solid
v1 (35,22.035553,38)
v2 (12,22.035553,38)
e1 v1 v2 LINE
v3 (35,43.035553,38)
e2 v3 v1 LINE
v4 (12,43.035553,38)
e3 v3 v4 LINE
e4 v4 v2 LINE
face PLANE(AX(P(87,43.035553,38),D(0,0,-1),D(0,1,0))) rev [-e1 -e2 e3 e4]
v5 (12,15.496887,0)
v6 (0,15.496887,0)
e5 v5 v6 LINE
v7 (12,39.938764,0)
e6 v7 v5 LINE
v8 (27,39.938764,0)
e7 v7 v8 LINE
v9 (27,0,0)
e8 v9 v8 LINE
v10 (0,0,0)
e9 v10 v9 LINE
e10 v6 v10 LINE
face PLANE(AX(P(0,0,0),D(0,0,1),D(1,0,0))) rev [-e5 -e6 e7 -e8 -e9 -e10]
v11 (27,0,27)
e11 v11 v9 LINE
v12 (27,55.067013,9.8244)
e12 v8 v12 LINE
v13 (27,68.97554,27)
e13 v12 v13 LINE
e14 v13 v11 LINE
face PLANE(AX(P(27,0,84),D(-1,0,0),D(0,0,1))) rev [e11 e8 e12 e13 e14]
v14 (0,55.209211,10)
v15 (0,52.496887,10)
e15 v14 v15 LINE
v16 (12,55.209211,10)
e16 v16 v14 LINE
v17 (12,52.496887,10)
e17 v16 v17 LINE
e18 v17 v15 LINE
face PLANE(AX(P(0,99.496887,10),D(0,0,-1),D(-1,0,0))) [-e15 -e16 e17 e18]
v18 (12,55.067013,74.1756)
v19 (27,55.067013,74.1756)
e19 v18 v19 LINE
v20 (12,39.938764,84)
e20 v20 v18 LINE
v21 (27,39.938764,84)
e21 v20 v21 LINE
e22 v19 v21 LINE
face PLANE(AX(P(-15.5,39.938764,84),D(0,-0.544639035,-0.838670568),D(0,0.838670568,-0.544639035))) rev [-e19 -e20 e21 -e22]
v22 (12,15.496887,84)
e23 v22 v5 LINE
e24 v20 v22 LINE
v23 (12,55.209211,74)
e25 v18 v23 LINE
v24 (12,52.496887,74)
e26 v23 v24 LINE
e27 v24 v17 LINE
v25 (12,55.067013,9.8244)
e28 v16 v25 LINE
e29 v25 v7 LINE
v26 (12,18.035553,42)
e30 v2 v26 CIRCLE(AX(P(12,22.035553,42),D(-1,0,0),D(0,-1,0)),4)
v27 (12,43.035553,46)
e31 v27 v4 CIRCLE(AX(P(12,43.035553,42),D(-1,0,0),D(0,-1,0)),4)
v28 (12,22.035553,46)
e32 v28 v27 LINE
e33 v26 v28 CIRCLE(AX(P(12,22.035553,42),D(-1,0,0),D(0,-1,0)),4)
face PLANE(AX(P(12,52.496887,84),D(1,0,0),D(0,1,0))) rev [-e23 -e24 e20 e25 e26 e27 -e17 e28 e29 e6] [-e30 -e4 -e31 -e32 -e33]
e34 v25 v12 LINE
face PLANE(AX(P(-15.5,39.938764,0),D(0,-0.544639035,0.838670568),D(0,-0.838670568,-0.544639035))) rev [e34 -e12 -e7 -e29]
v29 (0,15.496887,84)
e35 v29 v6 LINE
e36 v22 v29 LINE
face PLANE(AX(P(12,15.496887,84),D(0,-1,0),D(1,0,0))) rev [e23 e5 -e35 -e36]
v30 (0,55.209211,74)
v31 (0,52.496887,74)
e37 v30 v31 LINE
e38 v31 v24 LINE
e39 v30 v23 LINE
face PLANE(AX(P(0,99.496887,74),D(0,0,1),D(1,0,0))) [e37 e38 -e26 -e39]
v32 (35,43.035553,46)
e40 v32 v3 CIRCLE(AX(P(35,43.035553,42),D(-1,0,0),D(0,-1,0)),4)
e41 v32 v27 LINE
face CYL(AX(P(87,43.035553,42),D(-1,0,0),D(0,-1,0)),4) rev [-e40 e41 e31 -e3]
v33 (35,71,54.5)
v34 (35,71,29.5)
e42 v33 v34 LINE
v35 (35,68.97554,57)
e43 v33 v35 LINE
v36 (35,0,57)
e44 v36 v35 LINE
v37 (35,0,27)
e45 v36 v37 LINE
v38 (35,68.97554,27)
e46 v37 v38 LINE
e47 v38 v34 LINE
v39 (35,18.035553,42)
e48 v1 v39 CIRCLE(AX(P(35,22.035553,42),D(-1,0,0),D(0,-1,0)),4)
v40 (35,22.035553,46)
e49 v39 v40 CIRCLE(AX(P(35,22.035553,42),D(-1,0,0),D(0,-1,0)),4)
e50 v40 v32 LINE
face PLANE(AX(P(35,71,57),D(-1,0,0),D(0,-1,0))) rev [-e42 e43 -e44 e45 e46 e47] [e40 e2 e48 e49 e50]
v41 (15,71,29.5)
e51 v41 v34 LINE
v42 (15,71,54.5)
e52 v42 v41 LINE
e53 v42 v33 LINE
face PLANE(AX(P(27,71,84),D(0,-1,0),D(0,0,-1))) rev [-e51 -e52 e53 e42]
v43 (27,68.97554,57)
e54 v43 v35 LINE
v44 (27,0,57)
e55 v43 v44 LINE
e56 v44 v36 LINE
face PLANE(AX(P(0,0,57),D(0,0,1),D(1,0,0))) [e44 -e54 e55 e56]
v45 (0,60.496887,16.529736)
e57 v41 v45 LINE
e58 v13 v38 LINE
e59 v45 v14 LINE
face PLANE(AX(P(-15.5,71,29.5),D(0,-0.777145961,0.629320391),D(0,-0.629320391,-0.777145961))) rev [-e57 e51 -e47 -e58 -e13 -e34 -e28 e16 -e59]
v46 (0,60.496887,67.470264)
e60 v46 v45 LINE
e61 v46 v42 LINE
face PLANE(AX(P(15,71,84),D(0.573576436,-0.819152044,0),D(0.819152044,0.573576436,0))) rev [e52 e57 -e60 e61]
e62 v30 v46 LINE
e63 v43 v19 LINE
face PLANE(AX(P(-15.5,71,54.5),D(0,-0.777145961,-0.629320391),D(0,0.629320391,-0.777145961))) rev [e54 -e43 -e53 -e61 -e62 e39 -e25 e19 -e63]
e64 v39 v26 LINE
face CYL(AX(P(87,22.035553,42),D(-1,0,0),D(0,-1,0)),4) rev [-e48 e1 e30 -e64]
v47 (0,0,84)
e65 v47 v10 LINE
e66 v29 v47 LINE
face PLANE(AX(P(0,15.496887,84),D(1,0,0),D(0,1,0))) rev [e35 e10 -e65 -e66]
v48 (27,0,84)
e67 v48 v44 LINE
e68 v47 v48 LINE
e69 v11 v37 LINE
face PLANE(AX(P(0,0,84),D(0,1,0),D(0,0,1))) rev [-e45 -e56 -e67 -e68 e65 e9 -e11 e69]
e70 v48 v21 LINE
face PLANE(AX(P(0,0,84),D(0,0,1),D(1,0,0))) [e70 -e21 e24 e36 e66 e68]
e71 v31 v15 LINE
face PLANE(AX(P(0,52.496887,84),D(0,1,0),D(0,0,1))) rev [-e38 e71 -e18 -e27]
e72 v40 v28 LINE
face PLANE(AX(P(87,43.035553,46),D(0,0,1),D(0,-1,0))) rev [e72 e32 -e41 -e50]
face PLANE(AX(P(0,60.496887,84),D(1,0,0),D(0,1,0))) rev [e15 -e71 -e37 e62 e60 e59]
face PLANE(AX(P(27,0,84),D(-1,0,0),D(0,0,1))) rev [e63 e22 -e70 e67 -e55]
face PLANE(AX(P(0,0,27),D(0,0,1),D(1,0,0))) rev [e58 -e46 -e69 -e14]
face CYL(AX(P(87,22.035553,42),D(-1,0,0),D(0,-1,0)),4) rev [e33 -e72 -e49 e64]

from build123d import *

# Parameters (mm, degrees)
BASE_BLOCK_84MM_DEPTH  = 84
BACK_CHANNEL_SKETCH_W  = 12
BACK_CHANNEL_SKETCH_H  = 10
BACK_CHANNEL_CUT_DEPTH = 84
FRONT_PAD_SKETCH_W     = 8
FRONT_PAD_SKETCH_H     = 71
FRONT_PAD_8MM_DEPTH    = 15
TOP_CHAMFER_CUT_DEPTH  = 42.5
SLOT_CUT_DEPTH         = 75


with BuildPart() as part:
    # Block Profile Sketch → Base Block 84mm (new body)
    with BuildSketch(Plane.XY):
        Polygon((0, 0), (27, 0), (27, 71), (15, 71), (0, 60.496886927), (0, 52.496886927), (12, 52.496886927), (12, 15.496886927), (0, 15.496886927), align=None)
    extrude(amount=BASE_BLOCK_84MM_DEPTH)

    # Back Channel Sketch → Back Channel Cut (cut)
    with BuildSketch(Plane(origin=(0, 15.496886927, 0), x_dir=(1, 0, 0), z_dir=(0, 1, 0))):
        with Locations((6, -79)):
            Rectangle(BACK_CHANNEL_SKETCH_W, BACK_CHANNEL_SKETCH_H)
        with Locations((6, -5)):
            Rectangle(BACK_CHANNEL_SKETCH_W, BACK_CHANNEL_SKETCH_H)
    extrude(amount=BACK_CHANNEL_CUT_DEPTH, mode=Mode.SUBTRACT)

    # Front Pad Sketch → Front Pad 8mm (add, symmetric)
    with BuildSketch(Plane.XY.offset(42)):
        with Locations((31, 35.5)):
            Rectangle(FRONT_PAD_SKETCH_W, FRONT_PAD_SKETCH_H)
    extrude(amount=FRONT_PAD_8MM_DEPTH, both=True)

    # Top Chamfer Sketch → Top Chamfer Cut (cut, symmetric)
    with BuildSketch(Plane(origin=(27, 0, 0), x_dir=(0, 0, -1), z_dir=(1, 0, 0))):
        Polygon((-54.5, 71), (-74.175600087, 55.067013206), (-84, 39.938763989), (-84, 71), align=None)
        Polygon((-29.5, 71), (-9.824399913, 55.067013206), (0, 39.938763989), (0, 71), align=None)
    extrude(amount=TOP_CHAMFER_CUT_DEPTH, both=True, mode=Mode.SUBTRACT)

    # Slot Sketch → Slot Cut (cut)
    with BuildSketch(Plane.ZY.offset(-12)):
        with BuildLine():
            Line((46, 43.035553087), (46, 22.035553087))
            ThreePointArc((46, 22.035553087), (42, 18.035553087), (38, 22.035553087))
            Line((38, 22.035553087), (38, 43.035553087))
            ThreePointArc((38, 43.035553087), (42, 47.035553087), (46, 43.035553087))
        make_face()
    extrude(amount=-SLOT_CUT_DEPTH, mode=Mode.SUBTRACT)


solid = part.part
